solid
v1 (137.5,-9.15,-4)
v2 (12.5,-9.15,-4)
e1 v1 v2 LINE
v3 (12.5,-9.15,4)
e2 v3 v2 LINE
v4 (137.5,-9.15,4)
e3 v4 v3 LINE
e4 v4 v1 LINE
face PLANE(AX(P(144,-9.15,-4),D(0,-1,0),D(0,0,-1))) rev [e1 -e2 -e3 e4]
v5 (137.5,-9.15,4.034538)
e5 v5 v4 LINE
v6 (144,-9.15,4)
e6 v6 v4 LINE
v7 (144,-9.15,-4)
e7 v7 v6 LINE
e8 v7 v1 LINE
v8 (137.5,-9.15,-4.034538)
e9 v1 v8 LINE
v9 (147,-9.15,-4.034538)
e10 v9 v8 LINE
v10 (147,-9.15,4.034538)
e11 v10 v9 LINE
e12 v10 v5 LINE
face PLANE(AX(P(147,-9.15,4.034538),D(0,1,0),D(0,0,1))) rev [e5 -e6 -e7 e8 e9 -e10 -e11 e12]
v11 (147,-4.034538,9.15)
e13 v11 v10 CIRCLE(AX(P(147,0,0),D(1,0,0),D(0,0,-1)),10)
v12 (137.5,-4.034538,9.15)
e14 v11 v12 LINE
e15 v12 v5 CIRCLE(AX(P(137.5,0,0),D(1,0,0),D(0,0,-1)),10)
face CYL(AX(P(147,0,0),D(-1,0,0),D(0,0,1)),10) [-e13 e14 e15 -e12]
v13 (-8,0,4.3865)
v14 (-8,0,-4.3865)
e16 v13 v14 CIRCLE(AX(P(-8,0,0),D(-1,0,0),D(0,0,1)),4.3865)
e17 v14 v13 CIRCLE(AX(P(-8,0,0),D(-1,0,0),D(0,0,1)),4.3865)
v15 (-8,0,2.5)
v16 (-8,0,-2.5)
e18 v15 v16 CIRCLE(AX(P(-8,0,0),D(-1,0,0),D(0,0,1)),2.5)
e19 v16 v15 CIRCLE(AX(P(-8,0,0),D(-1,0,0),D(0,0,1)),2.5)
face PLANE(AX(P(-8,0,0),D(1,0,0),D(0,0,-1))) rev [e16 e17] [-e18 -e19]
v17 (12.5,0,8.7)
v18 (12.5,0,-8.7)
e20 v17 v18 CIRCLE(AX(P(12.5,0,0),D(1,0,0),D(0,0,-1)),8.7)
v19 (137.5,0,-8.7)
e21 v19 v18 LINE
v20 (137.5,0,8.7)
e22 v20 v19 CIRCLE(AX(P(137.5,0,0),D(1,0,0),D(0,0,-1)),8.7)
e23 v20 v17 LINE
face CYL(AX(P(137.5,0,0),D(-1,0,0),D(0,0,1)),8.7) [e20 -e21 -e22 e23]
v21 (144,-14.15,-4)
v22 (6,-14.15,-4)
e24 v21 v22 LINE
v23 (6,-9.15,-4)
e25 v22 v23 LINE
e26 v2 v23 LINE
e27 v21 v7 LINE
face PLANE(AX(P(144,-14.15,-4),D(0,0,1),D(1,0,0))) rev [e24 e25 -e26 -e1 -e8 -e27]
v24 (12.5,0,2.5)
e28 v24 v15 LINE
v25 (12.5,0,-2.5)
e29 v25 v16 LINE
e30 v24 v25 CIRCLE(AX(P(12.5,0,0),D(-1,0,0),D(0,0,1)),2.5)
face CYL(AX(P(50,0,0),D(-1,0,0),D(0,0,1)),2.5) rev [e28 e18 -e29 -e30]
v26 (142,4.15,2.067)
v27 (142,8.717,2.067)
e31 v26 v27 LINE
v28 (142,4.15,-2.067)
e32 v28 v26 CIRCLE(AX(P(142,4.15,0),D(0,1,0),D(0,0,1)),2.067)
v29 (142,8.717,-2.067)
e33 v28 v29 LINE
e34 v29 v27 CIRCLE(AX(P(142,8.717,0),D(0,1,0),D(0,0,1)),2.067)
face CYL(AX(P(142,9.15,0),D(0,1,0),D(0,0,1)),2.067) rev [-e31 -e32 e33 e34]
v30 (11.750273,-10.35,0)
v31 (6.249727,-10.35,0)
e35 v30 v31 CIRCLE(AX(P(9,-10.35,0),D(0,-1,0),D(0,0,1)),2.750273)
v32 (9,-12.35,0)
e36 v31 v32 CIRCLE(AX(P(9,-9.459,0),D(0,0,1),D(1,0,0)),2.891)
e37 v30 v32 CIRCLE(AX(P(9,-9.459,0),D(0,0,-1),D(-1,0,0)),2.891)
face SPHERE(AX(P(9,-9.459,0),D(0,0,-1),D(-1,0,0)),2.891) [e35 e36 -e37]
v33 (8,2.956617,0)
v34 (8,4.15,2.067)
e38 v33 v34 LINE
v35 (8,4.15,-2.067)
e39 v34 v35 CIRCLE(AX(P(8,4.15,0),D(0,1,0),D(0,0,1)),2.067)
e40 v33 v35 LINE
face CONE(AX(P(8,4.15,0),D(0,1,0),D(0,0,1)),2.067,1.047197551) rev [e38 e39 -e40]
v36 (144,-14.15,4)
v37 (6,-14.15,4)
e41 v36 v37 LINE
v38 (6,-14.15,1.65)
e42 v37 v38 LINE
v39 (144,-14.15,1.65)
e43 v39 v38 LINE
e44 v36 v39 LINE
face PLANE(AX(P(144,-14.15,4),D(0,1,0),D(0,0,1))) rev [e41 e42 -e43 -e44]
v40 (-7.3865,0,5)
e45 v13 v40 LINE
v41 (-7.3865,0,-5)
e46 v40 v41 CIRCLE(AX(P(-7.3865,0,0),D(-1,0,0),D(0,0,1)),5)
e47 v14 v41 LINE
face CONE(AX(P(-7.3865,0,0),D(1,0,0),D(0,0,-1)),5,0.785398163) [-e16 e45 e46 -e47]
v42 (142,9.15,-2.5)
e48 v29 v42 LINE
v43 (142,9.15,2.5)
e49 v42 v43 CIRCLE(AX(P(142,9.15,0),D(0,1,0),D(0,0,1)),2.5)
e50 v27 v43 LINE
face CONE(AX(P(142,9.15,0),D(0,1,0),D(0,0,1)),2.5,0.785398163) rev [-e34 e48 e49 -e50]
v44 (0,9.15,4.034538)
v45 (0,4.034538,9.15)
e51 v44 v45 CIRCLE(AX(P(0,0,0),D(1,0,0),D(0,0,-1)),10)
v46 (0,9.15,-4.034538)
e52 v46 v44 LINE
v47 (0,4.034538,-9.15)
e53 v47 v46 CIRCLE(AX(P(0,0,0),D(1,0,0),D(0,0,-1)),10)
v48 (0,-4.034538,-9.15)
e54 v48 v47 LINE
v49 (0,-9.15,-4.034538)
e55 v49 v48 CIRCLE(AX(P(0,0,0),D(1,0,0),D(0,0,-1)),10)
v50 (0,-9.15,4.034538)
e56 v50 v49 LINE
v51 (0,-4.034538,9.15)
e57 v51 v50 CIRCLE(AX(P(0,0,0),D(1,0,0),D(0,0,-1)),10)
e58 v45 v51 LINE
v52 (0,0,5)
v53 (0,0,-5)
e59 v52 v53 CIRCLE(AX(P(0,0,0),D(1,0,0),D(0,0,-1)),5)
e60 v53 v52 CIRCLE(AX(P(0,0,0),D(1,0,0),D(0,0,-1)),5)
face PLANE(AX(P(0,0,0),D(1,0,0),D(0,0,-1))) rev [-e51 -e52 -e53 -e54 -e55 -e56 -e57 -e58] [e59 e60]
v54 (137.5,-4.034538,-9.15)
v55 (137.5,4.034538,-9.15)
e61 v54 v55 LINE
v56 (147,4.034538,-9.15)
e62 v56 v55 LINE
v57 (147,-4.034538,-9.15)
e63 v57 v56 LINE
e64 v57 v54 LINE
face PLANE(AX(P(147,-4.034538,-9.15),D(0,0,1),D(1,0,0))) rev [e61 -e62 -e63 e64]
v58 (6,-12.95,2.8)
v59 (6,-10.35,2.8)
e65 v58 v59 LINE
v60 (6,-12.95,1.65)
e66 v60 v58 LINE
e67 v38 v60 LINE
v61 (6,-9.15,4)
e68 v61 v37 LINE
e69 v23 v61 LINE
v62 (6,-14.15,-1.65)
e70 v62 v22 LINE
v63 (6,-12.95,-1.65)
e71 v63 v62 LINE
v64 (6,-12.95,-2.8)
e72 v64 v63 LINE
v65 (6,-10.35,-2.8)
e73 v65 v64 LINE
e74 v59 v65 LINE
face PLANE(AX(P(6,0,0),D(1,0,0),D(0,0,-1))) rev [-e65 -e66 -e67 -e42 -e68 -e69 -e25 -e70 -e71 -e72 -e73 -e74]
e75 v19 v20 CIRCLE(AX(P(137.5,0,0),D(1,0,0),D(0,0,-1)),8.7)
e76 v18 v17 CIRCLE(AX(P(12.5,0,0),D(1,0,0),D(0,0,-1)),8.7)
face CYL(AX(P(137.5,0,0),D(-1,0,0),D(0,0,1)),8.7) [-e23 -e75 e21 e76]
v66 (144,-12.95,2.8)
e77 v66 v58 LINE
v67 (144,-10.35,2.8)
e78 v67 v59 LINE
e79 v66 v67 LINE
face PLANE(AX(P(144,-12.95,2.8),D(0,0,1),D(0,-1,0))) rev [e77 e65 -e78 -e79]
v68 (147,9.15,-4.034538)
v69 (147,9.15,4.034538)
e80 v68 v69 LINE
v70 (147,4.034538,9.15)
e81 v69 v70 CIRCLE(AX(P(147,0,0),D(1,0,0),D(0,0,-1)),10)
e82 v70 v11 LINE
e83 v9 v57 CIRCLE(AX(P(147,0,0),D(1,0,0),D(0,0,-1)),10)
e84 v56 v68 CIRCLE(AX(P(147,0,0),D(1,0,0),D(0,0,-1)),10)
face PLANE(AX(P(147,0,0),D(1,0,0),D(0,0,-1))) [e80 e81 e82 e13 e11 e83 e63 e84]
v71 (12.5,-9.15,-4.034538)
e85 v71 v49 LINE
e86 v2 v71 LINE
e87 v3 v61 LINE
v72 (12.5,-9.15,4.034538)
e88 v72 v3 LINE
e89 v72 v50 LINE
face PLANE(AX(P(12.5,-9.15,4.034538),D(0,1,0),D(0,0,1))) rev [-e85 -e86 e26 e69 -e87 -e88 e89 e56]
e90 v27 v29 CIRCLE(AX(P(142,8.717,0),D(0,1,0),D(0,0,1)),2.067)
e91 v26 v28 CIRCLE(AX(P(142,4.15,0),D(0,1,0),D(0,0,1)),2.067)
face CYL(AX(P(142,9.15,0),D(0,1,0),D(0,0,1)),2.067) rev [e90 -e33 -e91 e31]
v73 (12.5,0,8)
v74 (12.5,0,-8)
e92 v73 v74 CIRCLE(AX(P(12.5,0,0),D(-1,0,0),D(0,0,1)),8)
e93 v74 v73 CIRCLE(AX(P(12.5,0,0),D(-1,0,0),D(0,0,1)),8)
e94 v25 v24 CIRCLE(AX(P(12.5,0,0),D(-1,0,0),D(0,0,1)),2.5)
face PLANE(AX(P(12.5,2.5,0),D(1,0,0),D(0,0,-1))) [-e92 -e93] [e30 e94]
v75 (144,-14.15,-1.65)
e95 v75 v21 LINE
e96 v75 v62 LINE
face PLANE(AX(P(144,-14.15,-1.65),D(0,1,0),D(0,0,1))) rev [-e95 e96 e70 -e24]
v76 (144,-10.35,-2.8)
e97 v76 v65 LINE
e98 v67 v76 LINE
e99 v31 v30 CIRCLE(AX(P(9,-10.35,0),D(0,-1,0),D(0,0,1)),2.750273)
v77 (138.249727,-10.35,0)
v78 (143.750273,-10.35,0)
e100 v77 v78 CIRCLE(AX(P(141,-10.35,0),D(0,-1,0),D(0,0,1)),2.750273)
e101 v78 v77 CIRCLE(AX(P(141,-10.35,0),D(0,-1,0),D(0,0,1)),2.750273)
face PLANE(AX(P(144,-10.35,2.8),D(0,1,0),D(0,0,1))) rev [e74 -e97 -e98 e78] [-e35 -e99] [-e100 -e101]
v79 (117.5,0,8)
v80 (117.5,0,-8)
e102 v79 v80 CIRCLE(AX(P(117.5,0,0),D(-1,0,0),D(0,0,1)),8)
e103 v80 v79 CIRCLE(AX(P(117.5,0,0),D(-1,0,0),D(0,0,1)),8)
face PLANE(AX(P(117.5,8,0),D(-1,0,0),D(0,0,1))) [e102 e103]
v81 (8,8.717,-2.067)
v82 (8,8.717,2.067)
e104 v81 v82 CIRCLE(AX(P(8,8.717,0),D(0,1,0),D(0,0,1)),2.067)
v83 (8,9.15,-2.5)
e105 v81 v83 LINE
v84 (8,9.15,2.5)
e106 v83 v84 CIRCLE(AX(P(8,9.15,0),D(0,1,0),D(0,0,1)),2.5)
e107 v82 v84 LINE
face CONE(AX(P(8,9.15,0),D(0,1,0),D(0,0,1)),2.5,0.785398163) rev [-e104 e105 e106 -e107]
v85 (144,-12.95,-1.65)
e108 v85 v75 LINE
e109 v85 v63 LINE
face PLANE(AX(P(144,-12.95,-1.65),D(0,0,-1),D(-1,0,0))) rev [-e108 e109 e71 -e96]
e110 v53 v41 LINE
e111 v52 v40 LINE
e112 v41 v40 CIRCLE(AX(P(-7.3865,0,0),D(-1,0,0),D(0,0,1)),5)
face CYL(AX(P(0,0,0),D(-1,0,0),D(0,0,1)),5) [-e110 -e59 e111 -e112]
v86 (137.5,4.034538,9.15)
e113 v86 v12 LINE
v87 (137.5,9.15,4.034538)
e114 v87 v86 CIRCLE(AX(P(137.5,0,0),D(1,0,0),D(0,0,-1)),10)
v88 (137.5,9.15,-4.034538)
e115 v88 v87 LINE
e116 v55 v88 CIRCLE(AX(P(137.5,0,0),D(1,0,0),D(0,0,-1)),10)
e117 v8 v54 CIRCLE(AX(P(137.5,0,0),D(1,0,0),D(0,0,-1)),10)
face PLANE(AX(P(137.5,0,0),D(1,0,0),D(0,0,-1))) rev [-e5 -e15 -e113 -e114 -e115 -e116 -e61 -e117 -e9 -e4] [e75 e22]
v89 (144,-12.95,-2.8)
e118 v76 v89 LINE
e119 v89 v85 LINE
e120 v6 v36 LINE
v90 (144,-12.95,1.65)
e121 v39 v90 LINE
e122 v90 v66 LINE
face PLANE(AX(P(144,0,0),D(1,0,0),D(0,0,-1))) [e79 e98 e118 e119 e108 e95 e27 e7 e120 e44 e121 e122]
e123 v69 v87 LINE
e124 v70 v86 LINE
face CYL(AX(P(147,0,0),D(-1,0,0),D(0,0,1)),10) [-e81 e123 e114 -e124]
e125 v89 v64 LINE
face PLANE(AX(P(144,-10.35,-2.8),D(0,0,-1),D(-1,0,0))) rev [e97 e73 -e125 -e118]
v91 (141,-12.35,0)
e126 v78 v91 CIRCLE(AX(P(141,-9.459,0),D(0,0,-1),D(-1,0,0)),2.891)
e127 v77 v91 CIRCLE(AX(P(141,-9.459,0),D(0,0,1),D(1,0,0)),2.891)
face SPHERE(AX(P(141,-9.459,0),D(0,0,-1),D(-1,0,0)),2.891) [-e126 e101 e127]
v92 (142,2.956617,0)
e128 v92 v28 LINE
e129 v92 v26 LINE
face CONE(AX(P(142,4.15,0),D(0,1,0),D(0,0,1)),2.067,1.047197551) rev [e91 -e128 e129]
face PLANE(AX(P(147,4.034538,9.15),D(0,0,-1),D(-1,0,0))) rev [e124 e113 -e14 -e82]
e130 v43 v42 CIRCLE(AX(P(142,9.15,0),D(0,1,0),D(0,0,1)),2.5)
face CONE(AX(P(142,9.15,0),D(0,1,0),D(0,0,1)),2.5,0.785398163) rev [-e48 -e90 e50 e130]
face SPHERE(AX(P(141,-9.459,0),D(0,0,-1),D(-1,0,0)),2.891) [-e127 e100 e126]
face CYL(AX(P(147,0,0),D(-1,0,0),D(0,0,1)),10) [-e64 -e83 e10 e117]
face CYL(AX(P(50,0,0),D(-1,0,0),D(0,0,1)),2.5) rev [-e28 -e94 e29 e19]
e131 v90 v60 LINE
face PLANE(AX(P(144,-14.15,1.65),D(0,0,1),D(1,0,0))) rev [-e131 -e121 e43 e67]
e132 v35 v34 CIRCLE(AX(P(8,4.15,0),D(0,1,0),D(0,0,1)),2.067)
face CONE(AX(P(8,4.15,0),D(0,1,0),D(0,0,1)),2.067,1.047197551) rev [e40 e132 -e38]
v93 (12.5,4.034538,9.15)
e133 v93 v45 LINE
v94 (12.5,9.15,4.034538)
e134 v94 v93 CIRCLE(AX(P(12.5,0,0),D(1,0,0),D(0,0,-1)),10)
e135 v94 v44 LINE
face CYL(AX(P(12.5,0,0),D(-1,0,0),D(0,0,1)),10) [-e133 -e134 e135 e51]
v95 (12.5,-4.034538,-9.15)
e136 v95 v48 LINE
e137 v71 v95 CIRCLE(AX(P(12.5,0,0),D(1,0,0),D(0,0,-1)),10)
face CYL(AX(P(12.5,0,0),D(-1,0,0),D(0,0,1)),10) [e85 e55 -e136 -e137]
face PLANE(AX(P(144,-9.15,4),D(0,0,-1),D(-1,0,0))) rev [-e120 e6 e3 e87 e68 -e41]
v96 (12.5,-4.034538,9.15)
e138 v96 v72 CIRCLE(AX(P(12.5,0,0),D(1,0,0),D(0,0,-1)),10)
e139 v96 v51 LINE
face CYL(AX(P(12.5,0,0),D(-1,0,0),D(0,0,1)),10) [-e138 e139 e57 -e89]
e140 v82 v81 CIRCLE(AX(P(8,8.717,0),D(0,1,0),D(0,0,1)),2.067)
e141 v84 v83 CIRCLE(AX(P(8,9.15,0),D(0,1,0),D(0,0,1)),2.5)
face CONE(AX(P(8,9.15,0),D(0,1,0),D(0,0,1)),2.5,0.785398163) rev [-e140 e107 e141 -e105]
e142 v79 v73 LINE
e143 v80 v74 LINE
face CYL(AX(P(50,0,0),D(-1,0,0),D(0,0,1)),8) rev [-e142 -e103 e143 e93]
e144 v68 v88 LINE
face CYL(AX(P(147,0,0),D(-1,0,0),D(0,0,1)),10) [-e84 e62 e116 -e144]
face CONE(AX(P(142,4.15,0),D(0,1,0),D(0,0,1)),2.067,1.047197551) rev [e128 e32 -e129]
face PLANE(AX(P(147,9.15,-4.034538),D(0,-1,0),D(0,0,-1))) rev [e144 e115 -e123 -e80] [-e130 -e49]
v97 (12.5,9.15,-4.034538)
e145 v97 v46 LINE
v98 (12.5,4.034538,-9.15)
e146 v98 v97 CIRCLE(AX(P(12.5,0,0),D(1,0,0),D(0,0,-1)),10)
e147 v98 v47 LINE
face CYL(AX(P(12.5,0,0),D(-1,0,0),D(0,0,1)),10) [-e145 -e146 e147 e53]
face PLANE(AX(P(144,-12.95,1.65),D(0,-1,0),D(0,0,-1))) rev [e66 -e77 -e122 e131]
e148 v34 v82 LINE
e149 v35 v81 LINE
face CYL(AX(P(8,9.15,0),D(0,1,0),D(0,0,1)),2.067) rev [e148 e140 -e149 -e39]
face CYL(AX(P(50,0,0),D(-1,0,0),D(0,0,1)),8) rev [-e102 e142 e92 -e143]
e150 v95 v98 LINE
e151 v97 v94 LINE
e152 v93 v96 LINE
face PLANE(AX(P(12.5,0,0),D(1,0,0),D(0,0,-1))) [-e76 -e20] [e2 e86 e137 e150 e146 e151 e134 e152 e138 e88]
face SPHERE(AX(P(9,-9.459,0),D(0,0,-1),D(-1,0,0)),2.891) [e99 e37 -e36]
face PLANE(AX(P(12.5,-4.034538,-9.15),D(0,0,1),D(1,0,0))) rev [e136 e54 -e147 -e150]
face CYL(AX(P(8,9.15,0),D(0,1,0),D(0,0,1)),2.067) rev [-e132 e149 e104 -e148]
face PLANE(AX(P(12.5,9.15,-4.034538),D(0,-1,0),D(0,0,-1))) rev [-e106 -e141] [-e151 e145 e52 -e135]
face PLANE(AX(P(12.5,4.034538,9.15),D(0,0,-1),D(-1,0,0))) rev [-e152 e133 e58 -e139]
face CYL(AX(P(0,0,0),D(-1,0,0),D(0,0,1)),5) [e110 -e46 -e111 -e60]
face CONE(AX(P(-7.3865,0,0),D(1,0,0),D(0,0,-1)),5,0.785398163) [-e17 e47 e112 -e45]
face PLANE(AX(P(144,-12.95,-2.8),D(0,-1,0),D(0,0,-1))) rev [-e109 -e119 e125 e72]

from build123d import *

# Parameters (mm, degrees)
BOSS_EXTRUDE1_DEPTH   = 12.5
SKETCH3_R             = 8.7
BOSS_EXTRUDE2_DEPTH   = 125
BOSS_EXTRUDE3_DEPTH   = 9.5
HOLE1_D               = 4.134
HOLE1_DEPTH           = 5
HOLE1_CSINK_D         = 5
HOLE1_CSINK_ANGLE     = 90
HOLE1_TIP             = 1.193383006
HOLE2_D               = 4.134
HOLE2_DEPTH           = 5
HOLE2_CSINK_D         = 5
HOLE2_CSINK_ANGLE     = 90
HOLE2_TIP             = 1.193383006
BOSS_EXTRUDE4_DEPTH   = 138
LINEAR_PATTERN1_COUNT = 2
LINEAR_PATTERN1_PITCH = 132


with BuildPart() as part:
    # Sketch1 → Revolve1 (revolve)
    with BuildSketch(Plane.XY, mode=Mode.PRIVATE) as revolve1_sk:
        Polygon((-8, 0), (-8, 4.3865), (-7.3865, 5), (0, 5), (0, 0), align=None)
    revolve(revolve1_sk.sketch.rotate(Axis((0, 0, 0), (-1, 0, 0)), 270), axis=Axis((0, 0, 0), (-1, 0, 0)))

    # Sketch2 → Boss-Extrude1 (add)
    with BuildSketch(Plane(origin=(0, 0, 0), x_dir=(0, 0, -1), z_dir=(1, 0, 0))):
        with BuildLine():
            Line((-4.034538387, -9.15), (4.034538387, -9.15))
            ThreePointArc((4.034538387, -9.15), (7.071067812, -7.071067812), (9.15, -4.034538387))
            Line((9.15, -4.034538387), (9.15, 4.034538387))
            ThreePointArc((9.15, 4.034538387), (7.071067812, 7.071067812), (4.034538387, 9.15))
            Line((4.034538387, 9.15), (-4.034538387, 9.15))
            ThreePointArc((-4.034538387, 9.15), (-7.071067812, 7.071067812), (-9.15, 4.034538387))
            Line((-9.15, 4.034538387), (-9.15, -4.034538387))
            ThreePointArc((-9.15, -4.034538387), (-7.071067812, -7.071067812), (-4.034538387, -9.15))
        make_face()
    extrude(amount=BOSS_EXTRUDE1_DEPTH)

    # Sketch3 → Boss-Extrude2 (add)
    with BuildSketch(Plane(origin=(12.5, 0, 0), x_dir=(0, 0, -1), z_dir=(1, 0, 0))):
        Circle(SKETCH3_R)
    extrude(amount=BOSS_EXTRUDE2_DEPTH)

    # Sketch4 → Boss-Extrude3 (add)
    with BuildSketch(Plane(origin=(137.5, 0, 0), x_dir=(0, 0, -1), z_dir=(1, 0, 0))):
        with BuildLine():
            Line((-4.034538387, -9.15), (4.034538387, -9.15))
            ThreePointArc((4.034538387, -9.15), (7.071067812, -7.071067812), (9.15, -4.034538387))
            Line((9.15, -4.034538387), (9.15, 4.034538387))
            ThreePointArc((9.15, 4.034538387), (7.071067812, 7.071067812), (4.034538387, 9.15))
            Line((4.034538387, 9.15), (-4.034538387, 9.15))
            ThreePointArc((-4.034538387, 9.15), (-7.071067812, 7.071067812), (-9.15, 4.034538387))
            Line((-9.15, 4.034538387), (-9.15, -4.034538387))
            ThreePointArc((-9.15, -4.034538387), (-7.071067812, -7.071067812), (-4.034538387, -9.15))
        make_face()
    extrude(amount=BOSS_EXTRUDE3_DEPTH)

    # Hole1
    with Locations(Plane(origin=(0, 9.15, 0), x_dir=(1, 0, 0), z_dir=(0, 1, 0))):
        with Locations((8, 0)):
            CounterSinkHole(HOLE1_D / 2, HOLE1_CSINK_D / 2, depth=HOLE1_DEPTH, counter_sink_angle=HOLE1_CSINK_ANGLE)
            with Locations((0, 0, -(HOLE1_DEPTH + HOLE1_TIP / 2))):  # 120° drill point
                Cone(0, HOLE1_D / 2, HOLE1_TIP, mode=Mode.SUBTRACT)

    # Hole2
    with Locations(Plane(origin=(0, 9.15, 0), x_dir=(1, 0, 0), z_dir=(0, 1, 0))):
        with Locations((142, 0)):
            CounterSinkHole(HOLE2_D / 2, HOLE2_CSINK_D / 2, depth=HOLE2_DEPTH, counter_sink_angle=HOLE2_CSINK_ANGLE)
            with Locations((0, 0, -(HOLE2_DEPTH + HOLE2_TIP / 2))):  # 120° drill point
                Cone(0, HOLE2_D / 2, HOLE2_TIP, mode=Mode.SUBTRACT)

    # Sketch9 → Cut-Revolve1 (revolve, cut)
    with BuildSketch(Plane.XY, mode=Mode.PRIVATE) as cut_revolve1_sk:
        Polygon((-8, 0), (-8, 2.5), (12.5, 2.5), (12.5, 8), (117.5, 8), (117.5, 0), align=None)
    revolve(cut_revolve1_sk.sketch.rotate(Axis((50, 0, 0), (-1, 0, 0)), 270), axis=Axis((50, 0, 0), (-1, 0, 0)), mode=Mode.SUBTRACT)

    # Sketch10 → Boss-Extrude4 (add)
    with BuildSketch(Plane(origin=(6, 0, 0), x_dir=(0, 0, -1), z_dir=(1, 0, 0))):
        Polygon((-4, -9.15), (-4, -14.15), (-1.65, -14.15), (-1.65, -12.95), (-2.8, -12.95), (-2.8, -10.35), (2.8, -10.35), (2.8, -12.95), (1.65, -12.95), (1.65, -14.15), (4, -14.15), (4, -9.15), align=None)
    extrude(amount=BOSS_EXTRUDE4_DEPTH)

    # Sketch11 → Revolve2 (revolve)
    with BuildSketch(Plane.XY):
        with BuildLine():
            Line((6.249727286, -10.35), (9, -10.35))
            Line((9, -10.35), (9, -12.35))
            ThreePointArc((9, -12.35), (7.299705908, -11.797136224), (6.249727286, -10.35))
        make_face()
    revolve2 = revolve(axis=Axis((9, 50, 0), (0, -1, 0)))

    # Linear pattern1: Revolve2 ×2
    with Locations(*[(i * LINEAR_PATTERN1_PITCH, 0, 0) for i in range(1, LINEAR_PATTERN1_COUNT)]):
        add(revolve2)


solid = part.part
